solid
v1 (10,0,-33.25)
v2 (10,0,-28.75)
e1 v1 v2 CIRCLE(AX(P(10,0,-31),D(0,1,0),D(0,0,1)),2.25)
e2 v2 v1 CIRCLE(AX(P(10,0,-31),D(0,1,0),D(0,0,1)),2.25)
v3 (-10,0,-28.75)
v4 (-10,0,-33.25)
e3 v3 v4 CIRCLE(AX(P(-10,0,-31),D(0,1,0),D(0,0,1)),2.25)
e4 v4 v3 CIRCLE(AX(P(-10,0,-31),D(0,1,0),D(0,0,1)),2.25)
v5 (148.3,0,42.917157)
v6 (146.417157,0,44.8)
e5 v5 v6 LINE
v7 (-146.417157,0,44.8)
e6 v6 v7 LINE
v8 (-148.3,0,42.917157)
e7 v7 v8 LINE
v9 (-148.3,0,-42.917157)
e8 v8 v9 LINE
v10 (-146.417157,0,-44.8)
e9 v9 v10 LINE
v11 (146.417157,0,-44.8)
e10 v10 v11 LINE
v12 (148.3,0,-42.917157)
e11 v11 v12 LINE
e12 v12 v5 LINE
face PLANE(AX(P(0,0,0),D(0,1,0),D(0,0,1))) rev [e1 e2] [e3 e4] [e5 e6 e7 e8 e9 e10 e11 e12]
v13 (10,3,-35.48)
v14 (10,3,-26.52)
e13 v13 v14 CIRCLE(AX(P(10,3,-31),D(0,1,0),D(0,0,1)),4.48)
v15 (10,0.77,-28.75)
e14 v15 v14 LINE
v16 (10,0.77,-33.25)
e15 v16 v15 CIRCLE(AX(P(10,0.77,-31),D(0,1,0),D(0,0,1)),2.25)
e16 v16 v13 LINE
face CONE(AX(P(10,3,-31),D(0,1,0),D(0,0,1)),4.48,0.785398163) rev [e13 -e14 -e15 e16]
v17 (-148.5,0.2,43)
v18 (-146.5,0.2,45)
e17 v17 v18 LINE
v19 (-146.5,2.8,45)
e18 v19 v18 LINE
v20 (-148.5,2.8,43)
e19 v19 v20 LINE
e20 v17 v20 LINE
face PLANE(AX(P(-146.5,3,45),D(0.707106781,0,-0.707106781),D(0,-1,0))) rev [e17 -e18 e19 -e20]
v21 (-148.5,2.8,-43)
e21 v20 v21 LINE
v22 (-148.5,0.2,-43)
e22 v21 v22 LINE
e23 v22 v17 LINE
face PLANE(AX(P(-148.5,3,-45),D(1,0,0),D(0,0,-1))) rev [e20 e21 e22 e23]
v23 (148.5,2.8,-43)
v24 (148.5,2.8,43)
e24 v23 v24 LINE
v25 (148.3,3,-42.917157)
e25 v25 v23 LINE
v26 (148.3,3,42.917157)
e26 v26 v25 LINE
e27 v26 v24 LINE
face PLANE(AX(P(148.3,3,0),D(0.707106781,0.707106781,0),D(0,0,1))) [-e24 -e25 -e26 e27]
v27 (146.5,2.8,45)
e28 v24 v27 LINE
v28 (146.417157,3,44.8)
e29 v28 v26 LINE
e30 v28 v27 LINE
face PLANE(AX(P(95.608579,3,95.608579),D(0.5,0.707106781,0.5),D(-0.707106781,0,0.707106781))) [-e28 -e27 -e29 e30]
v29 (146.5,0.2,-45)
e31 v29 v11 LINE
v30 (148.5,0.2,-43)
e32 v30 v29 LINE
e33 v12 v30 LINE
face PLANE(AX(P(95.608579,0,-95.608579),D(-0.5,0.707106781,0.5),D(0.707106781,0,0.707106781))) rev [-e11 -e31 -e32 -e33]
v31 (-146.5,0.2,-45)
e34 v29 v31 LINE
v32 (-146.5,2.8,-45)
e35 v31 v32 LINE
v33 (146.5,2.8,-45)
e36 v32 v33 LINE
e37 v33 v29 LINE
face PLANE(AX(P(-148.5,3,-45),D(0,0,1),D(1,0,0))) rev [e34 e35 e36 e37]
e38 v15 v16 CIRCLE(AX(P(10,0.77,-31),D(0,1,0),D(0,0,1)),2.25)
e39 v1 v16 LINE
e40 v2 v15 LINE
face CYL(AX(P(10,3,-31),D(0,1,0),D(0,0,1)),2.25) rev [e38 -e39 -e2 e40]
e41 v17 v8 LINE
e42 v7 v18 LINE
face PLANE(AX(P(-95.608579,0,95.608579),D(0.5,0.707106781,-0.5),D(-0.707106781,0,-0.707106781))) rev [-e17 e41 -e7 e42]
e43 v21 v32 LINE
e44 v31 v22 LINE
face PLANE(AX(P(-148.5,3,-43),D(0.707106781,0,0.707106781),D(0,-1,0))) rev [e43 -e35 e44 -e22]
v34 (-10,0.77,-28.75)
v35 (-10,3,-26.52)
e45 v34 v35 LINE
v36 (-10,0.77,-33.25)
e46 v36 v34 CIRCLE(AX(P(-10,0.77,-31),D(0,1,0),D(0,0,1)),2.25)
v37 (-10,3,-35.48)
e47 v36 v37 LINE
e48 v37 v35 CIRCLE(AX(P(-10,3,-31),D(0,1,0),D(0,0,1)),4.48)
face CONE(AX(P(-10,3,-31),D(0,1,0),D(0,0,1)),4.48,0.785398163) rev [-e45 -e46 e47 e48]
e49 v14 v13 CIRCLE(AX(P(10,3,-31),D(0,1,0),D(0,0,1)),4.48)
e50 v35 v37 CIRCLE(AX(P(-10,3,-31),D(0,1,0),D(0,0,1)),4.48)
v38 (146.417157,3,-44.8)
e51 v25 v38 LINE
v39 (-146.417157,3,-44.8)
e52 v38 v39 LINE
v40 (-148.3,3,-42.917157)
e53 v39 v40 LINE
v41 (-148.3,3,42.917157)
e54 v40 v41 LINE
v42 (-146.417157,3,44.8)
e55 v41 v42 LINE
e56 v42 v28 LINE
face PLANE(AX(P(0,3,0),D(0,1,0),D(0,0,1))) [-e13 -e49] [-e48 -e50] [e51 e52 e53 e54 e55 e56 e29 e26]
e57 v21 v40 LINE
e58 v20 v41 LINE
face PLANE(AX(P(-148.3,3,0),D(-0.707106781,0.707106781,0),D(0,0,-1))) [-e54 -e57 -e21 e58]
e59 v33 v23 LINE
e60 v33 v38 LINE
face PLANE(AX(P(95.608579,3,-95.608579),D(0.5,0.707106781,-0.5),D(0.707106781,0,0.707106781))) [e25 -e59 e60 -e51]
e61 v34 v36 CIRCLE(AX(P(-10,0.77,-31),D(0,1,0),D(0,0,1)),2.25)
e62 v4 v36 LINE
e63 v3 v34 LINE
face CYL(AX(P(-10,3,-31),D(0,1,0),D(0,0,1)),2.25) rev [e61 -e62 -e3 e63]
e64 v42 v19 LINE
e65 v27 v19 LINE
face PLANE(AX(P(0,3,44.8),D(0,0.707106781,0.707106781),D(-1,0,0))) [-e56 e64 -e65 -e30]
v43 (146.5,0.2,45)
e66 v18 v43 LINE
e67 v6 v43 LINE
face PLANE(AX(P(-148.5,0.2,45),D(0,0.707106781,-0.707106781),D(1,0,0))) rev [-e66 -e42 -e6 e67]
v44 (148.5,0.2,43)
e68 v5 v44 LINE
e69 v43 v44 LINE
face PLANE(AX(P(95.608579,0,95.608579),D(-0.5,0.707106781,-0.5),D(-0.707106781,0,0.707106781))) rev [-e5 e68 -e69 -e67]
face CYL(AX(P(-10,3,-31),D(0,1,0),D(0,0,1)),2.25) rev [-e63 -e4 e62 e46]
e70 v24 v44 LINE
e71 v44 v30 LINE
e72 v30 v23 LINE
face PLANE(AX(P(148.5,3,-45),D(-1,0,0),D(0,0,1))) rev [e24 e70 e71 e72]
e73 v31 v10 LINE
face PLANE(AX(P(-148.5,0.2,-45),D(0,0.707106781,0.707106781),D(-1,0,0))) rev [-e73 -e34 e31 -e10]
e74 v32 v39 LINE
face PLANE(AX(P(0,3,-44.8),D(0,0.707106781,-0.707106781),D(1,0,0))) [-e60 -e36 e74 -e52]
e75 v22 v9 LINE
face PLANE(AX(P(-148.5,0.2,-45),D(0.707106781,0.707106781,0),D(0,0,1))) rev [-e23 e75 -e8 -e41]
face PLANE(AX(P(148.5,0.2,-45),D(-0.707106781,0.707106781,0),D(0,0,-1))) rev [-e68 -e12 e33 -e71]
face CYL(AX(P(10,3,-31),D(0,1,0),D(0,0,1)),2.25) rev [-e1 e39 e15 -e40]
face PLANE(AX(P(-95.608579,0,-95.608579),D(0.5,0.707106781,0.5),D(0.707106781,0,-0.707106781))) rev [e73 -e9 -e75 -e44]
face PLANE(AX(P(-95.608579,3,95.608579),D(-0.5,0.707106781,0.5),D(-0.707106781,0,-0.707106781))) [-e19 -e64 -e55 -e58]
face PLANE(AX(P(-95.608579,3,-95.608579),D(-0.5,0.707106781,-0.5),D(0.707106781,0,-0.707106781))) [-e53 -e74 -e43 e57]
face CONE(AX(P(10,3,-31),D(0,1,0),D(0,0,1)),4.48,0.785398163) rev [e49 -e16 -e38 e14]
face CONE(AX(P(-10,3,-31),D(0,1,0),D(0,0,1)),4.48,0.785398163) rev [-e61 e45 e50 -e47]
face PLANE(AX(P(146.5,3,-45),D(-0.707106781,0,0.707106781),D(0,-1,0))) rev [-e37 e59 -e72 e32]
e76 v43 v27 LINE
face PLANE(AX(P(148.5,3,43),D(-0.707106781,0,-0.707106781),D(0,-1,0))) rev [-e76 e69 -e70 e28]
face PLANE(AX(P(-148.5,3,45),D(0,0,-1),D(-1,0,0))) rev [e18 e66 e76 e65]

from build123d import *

# Parameters (mm, degrees)
SKETCH_1_W                  = 297
SKETCH_1_H                  = 90
EXTRUDE_1_DEPTH             = 3
HOLE_WIZARD_M4_1_AT_2_COUNT = 2
HOLE_WIZARD_M4_1_AT_2_PITCH = 20
CHAMFER_1_SIZE              = 2
CHAMFER_2_SIZE              = 0.2
CHAMFER_3_SIZE              = 0.2


with BuildPart() as part:
    # 草图1 → 凸台-拉伸1 (new body)
    with BuildSketch(Plane(origin=(0, 0, 0), x_dir=(1, 0, 0), z_dir=(0, 1, 0))):
        Rectangle(SKETCH_1_W, SKETCH_1_H)
    extrude(amount=EXTRUDE_1_DEPTH)

    # 草图2 → M4 六角凹锥坑螺钉的锥形沉头孔1 (revolve, cut)
    with BuildSketch(Plane(origin=(-10, 3, -31), x_dir=(0, 0, 1), z_dir=(1, 0, 0))):
        Polygon((0, 0), (0, 3), (2.25, 3), (2.25, 2.23), (4.48, 0), align=None)
    hole_wizard_m4_1 = revolve(axis=Axis((-10, 9.35, -31), (0, -1, 0)), mode=Mode.SUBTRACT)

    # M4 六角凹锥坑螺钉的锥形沉头孔1 at 2: M4 六角凹锥坑螺钉的锥形沉头孔1 ×2
    with Locations(*[(i * HOLE_WIZARD_M4_1_AT_2_PITCH, 0, 0) for i in range(1, HOLE_WIZARD_M4_1_AT_2_COUNT)]):
        add(hole_wizard_m4_1, mode=Mode.SUBTRACT)

    # 倒角1
    chamfer_1_edges = [part.edges().sort_by_distance(p)[0] for p in [
        (148.5, 1.5, 45),
        (-148.5, 1.5, 45),
        (-148.5, 1.5, -45),
        (148.5, 1.5, -45),
    ]]
    chamfer(chamfer_1_edges, length=CHAMFER_1_SIZE)

    # 倒角2
    chamfer_2_edges = [part.edges().sort_by_distance(p)[0] for p in [
        (0, 0, -45),
        (148.5, 0, 0),
        (0, 0, 45),
        (-148.5, 0, 0),
        (-147.5, 0, -44),
        (-147.5, 0, 44),
        (147.5, 0, 44),
        (147.5, 0, -44),
    ]]
    chamfer(chamfer_2_edges, length=CHAMFER_2_SIZE)

    # 倒角3
    chamfer_3_edges = [part.edges().sort_by_distance(p)[0] for p in [
        (0, 3, -45),
        (148.5, 3, 0),
        (-148.5, 3, 0),
        (0, 3, 45),
        (-147.5, 3, -44),
        (-147.5, 3, 44),
        (147.5, 3, 44),
        (147.5, 3, -44),
    ]]
    chamfer(chamfer_3_edges, length=CHAMFER_3_SIZE)


solid = part.part
